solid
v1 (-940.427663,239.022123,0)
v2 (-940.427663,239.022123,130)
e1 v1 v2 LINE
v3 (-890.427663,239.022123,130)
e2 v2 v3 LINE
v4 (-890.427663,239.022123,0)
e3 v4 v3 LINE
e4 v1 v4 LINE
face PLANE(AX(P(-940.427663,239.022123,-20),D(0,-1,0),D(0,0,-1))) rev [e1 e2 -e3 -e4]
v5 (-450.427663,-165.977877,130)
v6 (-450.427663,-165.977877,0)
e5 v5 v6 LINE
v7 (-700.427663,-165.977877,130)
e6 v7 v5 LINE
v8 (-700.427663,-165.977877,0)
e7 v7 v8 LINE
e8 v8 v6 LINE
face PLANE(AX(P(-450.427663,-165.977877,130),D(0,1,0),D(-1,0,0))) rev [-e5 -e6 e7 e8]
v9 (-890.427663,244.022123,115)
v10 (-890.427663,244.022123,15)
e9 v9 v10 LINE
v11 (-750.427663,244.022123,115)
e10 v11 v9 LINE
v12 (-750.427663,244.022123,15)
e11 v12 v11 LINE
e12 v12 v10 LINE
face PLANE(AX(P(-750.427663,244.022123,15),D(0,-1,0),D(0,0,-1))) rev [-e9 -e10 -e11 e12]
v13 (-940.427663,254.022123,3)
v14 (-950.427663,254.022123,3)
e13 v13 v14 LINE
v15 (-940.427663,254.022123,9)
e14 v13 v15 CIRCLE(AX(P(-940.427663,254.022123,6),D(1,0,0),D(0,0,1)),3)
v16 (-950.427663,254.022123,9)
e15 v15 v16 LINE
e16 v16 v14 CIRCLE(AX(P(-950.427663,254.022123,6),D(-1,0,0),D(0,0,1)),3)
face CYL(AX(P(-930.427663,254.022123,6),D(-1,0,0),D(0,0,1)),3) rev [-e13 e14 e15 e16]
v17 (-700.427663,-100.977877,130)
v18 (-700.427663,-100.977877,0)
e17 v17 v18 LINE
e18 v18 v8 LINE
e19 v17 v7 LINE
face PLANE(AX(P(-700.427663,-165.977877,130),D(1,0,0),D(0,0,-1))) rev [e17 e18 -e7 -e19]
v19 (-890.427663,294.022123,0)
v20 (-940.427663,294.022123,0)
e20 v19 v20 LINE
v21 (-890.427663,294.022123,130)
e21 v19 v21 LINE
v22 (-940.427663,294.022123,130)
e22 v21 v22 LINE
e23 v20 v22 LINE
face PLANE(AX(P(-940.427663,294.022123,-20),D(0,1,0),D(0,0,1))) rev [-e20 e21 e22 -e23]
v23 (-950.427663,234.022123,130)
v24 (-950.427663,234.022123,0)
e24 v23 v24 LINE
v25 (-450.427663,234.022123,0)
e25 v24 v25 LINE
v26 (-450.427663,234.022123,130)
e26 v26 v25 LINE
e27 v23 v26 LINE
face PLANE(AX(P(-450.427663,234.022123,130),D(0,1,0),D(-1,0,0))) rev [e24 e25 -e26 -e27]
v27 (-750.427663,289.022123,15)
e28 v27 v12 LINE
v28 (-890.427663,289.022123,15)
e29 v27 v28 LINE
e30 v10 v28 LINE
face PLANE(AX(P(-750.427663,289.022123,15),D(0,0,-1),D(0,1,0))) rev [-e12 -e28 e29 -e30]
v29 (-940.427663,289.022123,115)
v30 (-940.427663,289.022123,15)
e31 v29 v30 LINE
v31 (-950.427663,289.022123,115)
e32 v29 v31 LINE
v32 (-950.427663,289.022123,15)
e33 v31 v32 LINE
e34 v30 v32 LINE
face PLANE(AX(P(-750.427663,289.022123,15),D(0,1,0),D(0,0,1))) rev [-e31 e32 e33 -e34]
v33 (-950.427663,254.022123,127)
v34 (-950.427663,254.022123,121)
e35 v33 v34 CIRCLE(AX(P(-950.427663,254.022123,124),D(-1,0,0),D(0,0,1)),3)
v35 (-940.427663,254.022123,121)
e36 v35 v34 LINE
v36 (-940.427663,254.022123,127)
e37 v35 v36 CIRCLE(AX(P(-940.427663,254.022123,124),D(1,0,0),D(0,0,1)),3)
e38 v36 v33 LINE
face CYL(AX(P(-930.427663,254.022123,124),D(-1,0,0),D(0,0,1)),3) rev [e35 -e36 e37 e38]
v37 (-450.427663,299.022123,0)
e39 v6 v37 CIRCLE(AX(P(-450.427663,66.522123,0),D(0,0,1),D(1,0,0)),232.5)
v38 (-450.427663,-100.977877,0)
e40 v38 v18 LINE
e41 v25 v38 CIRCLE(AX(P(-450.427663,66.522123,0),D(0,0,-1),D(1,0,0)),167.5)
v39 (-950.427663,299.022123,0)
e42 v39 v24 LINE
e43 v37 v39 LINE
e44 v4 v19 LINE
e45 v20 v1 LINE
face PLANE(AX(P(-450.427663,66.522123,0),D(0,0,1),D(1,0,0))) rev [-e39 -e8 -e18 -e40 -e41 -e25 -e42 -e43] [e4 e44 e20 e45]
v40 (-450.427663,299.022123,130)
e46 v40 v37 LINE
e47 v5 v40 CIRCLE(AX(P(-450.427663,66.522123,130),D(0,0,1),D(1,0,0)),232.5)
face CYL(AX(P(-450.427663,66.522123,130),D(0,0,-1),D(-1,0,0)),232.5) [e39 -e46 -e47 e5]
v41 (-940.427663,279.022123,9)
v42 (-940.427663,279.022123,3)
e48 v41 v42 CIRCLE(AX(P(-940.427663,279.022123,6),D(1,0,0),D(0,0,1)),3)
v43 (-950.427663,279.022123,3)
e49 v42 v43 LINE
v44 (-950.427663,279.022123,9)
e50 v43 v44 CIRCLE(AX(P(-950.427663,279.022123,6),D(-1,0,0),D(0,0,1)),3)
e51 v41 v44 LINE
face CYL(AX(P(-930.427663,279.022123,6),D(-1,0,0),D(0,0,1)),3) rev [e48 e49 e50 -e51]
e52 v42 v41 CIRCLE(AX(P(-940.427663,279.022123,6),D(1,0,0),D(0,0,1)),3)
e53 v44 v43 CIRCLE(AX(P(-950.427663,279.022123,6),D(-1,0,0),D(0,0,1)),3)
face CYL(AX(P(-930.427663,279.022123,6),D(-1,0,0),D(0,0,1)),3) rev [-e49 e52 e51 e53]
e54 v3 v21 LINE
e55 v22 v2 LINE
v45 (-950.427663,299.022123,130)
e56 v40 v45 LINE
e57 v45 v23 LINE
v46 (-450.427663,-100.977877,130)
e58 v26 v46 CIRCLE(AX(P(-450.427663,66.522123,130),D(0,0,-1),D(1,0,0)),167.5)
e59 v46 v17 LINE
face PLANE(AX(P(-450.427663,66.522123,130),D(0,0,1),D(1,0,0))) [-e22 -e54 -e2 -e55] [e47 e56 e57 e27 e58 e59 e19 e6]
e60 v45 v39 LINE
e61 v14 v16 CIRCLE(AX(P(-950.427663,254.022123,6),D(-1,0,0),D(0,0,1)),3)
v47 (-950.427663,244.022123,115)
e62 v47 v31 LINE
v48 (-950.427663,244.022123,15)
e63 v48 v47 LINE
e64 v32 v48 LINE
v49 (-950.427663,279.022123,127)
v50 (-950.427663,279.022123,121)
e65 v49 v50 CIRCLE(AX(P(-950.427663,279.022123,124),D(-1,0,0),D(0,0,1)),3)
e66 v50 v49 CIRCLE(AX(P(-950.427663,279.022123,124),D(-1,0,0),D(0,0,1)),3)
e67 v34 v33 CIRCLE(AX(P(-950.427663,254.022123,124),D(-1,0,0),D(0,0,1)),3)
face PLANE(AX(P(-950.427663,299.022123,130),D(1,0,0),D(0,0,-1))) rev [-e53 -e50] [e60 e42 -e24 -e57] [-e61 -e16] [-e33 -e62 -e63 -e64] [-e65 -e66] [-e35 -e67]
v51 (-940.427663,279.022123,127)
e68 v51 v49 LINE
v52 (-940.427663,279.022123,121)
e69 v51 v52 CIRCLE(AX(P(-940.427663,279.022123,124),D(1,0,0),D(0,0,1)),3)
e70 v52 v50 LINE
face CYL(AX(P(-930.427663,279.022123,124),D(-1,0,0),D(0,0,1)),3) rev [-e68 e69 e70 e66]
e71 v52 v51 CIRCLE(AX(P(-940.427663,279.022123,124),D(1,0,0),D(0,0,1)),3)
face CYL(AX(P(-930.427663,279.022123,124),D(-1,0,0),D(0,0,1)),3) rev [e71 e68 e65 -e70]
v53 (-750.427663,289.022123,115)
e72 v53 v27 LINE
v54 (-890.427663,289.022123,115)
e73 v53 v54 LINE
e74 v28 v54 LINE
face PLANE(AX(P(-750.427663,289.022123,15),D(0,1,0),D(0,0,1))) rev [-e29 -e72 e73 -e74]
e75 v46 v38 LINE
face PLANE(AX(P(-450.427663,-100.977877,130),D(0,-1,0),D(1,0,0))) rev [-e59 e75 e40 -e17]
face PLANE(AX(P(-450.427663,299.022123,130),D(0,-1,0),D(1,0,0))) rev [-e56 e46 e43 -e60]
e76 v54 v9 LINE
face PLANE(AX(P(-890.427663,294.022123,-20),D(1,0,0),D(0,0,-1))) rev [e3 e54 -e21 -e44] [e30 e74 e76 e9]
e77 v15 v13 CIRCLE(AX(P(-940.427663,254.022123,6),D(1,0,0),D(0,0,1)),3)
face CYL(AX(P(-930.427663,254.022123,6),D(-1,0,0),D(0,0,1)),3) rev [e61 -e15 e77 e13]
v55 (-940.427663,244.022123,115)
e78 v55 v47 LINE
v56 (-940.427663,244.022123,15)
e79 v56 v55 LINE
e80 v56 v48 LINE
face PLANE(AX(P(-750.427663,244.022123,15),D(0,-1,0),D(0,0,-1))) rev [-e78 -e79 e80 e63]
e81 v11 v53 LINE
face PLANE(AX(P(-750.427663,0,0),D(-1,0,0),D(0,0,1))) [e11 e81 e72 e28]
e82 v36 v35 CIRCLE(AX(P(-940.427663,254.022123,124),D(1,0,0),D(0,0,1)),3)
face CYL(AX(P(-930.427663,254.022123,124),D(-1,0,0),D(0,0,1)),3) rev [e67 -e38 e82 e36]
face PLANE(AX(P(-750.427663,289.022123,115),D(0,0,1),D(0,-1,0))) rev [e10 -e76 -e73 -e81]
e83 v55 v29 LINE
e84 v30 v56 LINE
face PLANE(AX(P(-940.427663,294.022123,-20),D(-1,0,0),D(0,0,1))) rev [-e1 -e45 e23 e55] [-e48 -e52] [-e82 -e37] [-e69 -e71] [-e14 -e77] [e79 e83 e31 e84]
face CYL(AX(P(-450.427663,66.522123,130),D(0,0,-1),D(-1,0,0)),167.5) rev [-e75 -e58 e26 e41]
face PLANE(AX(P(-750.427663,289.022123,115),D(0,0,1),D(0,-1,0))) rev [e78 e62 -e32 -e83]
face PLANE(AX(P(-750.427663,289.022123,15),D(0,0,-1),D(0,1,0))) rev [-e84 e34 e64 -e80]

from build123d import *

# Parameters (mm, degrees)
EXTRUDE_1_DEPTH     = 130
SKETCH_2_R          = 3
CUT_EXTRUDE_1_DEPTH = 20
SKETCH_9_W          = 50
SKETCH_9_H          = 55
CUT_EXTRUDE_2_DEPTH = 150
SKETCH_10_W         = 100
SKETCH_10_H         = 45
CUT_EXTRUDE_3_DEPTH = 200


with BuildPart() as part:
    # 草图1 → 凸台-拉伸1 (new body)
    with BuildSketch(Plane.XY):
        with BuildLine():
            Line((-450.427662897, 234.022122697), (-950.427662897, 234.022122697))
            Line((-950.427662897, 234.022122697), (-950.427662897, 299.022122697))
            Line((-950.427662897, 299.022122697), (-450.427662897, 299.022122697))
            ThreePointArc((-450.427662897, 299.022122697), (-217.927662897, 66.522122697), (-450.427662897, -165.977877303))
            Line((-450.427662897, -165.977877303), (-700.427662897, -165.977877303))
            Line((-700.427662897, -165.977877303), (-700.427662897, -100.977877303))
            Line((-700.427662897, -100.977877303), (-450.427662897, -100.977877303))
            ThreePointArc((-450.427662897, -100.977877303), (-282.927662897, 66.522122697), (-450.427662897, 234.022122697))
        make_face()
    extrude(amount=EXTRUDE_1_DEPTH)

    # 草图2 → 切除-拉伸1 (cut)
    with BuildSketch(Plane.ZY.offset(950.427662897)):
        with Locations((6, 279.022122697)):
            Circle(SKETCH_2_R)
        with Locations((6, 254.022122697)):
            Circle(SKETCH_2_R)
        with Locations((124, 279.022122697)):
            Circle(SKETCH_2_R)
        with Locations((124, 254.022122697)):
            Circle(SKETCH_2_R)
    extrude(amount=-CUT_EXTRUDE_1_DEPTH, mode=Mode.SUBTRACT)

    # 草图9 → 切除-拉伸2 (cut)
    with BuildSketch(Plane.XY.offset(130)):
        with Locations((-915.427662897, 266.522122697)):
            Rectangle(SKETCH_9_W, SKETCH_9_H)
    extrude(amount=-CUT_EXTRUDE_2_DEPTH, mode=Mode.SUBTRACT)

    # 草图10 → 切除-拉伸3 (cut)
    with BuildSketch(Plane.ZY.offset(950.427662897)):
        with Locations((65, 266.522122697)):
            Rectangle(SKETCH_10_W, SKETCH_10_H)
    extrude(amount=-CUT_EXTRUDE_3_DEPTH, mode=Mode.SUBTRACT)


solid = part.part
